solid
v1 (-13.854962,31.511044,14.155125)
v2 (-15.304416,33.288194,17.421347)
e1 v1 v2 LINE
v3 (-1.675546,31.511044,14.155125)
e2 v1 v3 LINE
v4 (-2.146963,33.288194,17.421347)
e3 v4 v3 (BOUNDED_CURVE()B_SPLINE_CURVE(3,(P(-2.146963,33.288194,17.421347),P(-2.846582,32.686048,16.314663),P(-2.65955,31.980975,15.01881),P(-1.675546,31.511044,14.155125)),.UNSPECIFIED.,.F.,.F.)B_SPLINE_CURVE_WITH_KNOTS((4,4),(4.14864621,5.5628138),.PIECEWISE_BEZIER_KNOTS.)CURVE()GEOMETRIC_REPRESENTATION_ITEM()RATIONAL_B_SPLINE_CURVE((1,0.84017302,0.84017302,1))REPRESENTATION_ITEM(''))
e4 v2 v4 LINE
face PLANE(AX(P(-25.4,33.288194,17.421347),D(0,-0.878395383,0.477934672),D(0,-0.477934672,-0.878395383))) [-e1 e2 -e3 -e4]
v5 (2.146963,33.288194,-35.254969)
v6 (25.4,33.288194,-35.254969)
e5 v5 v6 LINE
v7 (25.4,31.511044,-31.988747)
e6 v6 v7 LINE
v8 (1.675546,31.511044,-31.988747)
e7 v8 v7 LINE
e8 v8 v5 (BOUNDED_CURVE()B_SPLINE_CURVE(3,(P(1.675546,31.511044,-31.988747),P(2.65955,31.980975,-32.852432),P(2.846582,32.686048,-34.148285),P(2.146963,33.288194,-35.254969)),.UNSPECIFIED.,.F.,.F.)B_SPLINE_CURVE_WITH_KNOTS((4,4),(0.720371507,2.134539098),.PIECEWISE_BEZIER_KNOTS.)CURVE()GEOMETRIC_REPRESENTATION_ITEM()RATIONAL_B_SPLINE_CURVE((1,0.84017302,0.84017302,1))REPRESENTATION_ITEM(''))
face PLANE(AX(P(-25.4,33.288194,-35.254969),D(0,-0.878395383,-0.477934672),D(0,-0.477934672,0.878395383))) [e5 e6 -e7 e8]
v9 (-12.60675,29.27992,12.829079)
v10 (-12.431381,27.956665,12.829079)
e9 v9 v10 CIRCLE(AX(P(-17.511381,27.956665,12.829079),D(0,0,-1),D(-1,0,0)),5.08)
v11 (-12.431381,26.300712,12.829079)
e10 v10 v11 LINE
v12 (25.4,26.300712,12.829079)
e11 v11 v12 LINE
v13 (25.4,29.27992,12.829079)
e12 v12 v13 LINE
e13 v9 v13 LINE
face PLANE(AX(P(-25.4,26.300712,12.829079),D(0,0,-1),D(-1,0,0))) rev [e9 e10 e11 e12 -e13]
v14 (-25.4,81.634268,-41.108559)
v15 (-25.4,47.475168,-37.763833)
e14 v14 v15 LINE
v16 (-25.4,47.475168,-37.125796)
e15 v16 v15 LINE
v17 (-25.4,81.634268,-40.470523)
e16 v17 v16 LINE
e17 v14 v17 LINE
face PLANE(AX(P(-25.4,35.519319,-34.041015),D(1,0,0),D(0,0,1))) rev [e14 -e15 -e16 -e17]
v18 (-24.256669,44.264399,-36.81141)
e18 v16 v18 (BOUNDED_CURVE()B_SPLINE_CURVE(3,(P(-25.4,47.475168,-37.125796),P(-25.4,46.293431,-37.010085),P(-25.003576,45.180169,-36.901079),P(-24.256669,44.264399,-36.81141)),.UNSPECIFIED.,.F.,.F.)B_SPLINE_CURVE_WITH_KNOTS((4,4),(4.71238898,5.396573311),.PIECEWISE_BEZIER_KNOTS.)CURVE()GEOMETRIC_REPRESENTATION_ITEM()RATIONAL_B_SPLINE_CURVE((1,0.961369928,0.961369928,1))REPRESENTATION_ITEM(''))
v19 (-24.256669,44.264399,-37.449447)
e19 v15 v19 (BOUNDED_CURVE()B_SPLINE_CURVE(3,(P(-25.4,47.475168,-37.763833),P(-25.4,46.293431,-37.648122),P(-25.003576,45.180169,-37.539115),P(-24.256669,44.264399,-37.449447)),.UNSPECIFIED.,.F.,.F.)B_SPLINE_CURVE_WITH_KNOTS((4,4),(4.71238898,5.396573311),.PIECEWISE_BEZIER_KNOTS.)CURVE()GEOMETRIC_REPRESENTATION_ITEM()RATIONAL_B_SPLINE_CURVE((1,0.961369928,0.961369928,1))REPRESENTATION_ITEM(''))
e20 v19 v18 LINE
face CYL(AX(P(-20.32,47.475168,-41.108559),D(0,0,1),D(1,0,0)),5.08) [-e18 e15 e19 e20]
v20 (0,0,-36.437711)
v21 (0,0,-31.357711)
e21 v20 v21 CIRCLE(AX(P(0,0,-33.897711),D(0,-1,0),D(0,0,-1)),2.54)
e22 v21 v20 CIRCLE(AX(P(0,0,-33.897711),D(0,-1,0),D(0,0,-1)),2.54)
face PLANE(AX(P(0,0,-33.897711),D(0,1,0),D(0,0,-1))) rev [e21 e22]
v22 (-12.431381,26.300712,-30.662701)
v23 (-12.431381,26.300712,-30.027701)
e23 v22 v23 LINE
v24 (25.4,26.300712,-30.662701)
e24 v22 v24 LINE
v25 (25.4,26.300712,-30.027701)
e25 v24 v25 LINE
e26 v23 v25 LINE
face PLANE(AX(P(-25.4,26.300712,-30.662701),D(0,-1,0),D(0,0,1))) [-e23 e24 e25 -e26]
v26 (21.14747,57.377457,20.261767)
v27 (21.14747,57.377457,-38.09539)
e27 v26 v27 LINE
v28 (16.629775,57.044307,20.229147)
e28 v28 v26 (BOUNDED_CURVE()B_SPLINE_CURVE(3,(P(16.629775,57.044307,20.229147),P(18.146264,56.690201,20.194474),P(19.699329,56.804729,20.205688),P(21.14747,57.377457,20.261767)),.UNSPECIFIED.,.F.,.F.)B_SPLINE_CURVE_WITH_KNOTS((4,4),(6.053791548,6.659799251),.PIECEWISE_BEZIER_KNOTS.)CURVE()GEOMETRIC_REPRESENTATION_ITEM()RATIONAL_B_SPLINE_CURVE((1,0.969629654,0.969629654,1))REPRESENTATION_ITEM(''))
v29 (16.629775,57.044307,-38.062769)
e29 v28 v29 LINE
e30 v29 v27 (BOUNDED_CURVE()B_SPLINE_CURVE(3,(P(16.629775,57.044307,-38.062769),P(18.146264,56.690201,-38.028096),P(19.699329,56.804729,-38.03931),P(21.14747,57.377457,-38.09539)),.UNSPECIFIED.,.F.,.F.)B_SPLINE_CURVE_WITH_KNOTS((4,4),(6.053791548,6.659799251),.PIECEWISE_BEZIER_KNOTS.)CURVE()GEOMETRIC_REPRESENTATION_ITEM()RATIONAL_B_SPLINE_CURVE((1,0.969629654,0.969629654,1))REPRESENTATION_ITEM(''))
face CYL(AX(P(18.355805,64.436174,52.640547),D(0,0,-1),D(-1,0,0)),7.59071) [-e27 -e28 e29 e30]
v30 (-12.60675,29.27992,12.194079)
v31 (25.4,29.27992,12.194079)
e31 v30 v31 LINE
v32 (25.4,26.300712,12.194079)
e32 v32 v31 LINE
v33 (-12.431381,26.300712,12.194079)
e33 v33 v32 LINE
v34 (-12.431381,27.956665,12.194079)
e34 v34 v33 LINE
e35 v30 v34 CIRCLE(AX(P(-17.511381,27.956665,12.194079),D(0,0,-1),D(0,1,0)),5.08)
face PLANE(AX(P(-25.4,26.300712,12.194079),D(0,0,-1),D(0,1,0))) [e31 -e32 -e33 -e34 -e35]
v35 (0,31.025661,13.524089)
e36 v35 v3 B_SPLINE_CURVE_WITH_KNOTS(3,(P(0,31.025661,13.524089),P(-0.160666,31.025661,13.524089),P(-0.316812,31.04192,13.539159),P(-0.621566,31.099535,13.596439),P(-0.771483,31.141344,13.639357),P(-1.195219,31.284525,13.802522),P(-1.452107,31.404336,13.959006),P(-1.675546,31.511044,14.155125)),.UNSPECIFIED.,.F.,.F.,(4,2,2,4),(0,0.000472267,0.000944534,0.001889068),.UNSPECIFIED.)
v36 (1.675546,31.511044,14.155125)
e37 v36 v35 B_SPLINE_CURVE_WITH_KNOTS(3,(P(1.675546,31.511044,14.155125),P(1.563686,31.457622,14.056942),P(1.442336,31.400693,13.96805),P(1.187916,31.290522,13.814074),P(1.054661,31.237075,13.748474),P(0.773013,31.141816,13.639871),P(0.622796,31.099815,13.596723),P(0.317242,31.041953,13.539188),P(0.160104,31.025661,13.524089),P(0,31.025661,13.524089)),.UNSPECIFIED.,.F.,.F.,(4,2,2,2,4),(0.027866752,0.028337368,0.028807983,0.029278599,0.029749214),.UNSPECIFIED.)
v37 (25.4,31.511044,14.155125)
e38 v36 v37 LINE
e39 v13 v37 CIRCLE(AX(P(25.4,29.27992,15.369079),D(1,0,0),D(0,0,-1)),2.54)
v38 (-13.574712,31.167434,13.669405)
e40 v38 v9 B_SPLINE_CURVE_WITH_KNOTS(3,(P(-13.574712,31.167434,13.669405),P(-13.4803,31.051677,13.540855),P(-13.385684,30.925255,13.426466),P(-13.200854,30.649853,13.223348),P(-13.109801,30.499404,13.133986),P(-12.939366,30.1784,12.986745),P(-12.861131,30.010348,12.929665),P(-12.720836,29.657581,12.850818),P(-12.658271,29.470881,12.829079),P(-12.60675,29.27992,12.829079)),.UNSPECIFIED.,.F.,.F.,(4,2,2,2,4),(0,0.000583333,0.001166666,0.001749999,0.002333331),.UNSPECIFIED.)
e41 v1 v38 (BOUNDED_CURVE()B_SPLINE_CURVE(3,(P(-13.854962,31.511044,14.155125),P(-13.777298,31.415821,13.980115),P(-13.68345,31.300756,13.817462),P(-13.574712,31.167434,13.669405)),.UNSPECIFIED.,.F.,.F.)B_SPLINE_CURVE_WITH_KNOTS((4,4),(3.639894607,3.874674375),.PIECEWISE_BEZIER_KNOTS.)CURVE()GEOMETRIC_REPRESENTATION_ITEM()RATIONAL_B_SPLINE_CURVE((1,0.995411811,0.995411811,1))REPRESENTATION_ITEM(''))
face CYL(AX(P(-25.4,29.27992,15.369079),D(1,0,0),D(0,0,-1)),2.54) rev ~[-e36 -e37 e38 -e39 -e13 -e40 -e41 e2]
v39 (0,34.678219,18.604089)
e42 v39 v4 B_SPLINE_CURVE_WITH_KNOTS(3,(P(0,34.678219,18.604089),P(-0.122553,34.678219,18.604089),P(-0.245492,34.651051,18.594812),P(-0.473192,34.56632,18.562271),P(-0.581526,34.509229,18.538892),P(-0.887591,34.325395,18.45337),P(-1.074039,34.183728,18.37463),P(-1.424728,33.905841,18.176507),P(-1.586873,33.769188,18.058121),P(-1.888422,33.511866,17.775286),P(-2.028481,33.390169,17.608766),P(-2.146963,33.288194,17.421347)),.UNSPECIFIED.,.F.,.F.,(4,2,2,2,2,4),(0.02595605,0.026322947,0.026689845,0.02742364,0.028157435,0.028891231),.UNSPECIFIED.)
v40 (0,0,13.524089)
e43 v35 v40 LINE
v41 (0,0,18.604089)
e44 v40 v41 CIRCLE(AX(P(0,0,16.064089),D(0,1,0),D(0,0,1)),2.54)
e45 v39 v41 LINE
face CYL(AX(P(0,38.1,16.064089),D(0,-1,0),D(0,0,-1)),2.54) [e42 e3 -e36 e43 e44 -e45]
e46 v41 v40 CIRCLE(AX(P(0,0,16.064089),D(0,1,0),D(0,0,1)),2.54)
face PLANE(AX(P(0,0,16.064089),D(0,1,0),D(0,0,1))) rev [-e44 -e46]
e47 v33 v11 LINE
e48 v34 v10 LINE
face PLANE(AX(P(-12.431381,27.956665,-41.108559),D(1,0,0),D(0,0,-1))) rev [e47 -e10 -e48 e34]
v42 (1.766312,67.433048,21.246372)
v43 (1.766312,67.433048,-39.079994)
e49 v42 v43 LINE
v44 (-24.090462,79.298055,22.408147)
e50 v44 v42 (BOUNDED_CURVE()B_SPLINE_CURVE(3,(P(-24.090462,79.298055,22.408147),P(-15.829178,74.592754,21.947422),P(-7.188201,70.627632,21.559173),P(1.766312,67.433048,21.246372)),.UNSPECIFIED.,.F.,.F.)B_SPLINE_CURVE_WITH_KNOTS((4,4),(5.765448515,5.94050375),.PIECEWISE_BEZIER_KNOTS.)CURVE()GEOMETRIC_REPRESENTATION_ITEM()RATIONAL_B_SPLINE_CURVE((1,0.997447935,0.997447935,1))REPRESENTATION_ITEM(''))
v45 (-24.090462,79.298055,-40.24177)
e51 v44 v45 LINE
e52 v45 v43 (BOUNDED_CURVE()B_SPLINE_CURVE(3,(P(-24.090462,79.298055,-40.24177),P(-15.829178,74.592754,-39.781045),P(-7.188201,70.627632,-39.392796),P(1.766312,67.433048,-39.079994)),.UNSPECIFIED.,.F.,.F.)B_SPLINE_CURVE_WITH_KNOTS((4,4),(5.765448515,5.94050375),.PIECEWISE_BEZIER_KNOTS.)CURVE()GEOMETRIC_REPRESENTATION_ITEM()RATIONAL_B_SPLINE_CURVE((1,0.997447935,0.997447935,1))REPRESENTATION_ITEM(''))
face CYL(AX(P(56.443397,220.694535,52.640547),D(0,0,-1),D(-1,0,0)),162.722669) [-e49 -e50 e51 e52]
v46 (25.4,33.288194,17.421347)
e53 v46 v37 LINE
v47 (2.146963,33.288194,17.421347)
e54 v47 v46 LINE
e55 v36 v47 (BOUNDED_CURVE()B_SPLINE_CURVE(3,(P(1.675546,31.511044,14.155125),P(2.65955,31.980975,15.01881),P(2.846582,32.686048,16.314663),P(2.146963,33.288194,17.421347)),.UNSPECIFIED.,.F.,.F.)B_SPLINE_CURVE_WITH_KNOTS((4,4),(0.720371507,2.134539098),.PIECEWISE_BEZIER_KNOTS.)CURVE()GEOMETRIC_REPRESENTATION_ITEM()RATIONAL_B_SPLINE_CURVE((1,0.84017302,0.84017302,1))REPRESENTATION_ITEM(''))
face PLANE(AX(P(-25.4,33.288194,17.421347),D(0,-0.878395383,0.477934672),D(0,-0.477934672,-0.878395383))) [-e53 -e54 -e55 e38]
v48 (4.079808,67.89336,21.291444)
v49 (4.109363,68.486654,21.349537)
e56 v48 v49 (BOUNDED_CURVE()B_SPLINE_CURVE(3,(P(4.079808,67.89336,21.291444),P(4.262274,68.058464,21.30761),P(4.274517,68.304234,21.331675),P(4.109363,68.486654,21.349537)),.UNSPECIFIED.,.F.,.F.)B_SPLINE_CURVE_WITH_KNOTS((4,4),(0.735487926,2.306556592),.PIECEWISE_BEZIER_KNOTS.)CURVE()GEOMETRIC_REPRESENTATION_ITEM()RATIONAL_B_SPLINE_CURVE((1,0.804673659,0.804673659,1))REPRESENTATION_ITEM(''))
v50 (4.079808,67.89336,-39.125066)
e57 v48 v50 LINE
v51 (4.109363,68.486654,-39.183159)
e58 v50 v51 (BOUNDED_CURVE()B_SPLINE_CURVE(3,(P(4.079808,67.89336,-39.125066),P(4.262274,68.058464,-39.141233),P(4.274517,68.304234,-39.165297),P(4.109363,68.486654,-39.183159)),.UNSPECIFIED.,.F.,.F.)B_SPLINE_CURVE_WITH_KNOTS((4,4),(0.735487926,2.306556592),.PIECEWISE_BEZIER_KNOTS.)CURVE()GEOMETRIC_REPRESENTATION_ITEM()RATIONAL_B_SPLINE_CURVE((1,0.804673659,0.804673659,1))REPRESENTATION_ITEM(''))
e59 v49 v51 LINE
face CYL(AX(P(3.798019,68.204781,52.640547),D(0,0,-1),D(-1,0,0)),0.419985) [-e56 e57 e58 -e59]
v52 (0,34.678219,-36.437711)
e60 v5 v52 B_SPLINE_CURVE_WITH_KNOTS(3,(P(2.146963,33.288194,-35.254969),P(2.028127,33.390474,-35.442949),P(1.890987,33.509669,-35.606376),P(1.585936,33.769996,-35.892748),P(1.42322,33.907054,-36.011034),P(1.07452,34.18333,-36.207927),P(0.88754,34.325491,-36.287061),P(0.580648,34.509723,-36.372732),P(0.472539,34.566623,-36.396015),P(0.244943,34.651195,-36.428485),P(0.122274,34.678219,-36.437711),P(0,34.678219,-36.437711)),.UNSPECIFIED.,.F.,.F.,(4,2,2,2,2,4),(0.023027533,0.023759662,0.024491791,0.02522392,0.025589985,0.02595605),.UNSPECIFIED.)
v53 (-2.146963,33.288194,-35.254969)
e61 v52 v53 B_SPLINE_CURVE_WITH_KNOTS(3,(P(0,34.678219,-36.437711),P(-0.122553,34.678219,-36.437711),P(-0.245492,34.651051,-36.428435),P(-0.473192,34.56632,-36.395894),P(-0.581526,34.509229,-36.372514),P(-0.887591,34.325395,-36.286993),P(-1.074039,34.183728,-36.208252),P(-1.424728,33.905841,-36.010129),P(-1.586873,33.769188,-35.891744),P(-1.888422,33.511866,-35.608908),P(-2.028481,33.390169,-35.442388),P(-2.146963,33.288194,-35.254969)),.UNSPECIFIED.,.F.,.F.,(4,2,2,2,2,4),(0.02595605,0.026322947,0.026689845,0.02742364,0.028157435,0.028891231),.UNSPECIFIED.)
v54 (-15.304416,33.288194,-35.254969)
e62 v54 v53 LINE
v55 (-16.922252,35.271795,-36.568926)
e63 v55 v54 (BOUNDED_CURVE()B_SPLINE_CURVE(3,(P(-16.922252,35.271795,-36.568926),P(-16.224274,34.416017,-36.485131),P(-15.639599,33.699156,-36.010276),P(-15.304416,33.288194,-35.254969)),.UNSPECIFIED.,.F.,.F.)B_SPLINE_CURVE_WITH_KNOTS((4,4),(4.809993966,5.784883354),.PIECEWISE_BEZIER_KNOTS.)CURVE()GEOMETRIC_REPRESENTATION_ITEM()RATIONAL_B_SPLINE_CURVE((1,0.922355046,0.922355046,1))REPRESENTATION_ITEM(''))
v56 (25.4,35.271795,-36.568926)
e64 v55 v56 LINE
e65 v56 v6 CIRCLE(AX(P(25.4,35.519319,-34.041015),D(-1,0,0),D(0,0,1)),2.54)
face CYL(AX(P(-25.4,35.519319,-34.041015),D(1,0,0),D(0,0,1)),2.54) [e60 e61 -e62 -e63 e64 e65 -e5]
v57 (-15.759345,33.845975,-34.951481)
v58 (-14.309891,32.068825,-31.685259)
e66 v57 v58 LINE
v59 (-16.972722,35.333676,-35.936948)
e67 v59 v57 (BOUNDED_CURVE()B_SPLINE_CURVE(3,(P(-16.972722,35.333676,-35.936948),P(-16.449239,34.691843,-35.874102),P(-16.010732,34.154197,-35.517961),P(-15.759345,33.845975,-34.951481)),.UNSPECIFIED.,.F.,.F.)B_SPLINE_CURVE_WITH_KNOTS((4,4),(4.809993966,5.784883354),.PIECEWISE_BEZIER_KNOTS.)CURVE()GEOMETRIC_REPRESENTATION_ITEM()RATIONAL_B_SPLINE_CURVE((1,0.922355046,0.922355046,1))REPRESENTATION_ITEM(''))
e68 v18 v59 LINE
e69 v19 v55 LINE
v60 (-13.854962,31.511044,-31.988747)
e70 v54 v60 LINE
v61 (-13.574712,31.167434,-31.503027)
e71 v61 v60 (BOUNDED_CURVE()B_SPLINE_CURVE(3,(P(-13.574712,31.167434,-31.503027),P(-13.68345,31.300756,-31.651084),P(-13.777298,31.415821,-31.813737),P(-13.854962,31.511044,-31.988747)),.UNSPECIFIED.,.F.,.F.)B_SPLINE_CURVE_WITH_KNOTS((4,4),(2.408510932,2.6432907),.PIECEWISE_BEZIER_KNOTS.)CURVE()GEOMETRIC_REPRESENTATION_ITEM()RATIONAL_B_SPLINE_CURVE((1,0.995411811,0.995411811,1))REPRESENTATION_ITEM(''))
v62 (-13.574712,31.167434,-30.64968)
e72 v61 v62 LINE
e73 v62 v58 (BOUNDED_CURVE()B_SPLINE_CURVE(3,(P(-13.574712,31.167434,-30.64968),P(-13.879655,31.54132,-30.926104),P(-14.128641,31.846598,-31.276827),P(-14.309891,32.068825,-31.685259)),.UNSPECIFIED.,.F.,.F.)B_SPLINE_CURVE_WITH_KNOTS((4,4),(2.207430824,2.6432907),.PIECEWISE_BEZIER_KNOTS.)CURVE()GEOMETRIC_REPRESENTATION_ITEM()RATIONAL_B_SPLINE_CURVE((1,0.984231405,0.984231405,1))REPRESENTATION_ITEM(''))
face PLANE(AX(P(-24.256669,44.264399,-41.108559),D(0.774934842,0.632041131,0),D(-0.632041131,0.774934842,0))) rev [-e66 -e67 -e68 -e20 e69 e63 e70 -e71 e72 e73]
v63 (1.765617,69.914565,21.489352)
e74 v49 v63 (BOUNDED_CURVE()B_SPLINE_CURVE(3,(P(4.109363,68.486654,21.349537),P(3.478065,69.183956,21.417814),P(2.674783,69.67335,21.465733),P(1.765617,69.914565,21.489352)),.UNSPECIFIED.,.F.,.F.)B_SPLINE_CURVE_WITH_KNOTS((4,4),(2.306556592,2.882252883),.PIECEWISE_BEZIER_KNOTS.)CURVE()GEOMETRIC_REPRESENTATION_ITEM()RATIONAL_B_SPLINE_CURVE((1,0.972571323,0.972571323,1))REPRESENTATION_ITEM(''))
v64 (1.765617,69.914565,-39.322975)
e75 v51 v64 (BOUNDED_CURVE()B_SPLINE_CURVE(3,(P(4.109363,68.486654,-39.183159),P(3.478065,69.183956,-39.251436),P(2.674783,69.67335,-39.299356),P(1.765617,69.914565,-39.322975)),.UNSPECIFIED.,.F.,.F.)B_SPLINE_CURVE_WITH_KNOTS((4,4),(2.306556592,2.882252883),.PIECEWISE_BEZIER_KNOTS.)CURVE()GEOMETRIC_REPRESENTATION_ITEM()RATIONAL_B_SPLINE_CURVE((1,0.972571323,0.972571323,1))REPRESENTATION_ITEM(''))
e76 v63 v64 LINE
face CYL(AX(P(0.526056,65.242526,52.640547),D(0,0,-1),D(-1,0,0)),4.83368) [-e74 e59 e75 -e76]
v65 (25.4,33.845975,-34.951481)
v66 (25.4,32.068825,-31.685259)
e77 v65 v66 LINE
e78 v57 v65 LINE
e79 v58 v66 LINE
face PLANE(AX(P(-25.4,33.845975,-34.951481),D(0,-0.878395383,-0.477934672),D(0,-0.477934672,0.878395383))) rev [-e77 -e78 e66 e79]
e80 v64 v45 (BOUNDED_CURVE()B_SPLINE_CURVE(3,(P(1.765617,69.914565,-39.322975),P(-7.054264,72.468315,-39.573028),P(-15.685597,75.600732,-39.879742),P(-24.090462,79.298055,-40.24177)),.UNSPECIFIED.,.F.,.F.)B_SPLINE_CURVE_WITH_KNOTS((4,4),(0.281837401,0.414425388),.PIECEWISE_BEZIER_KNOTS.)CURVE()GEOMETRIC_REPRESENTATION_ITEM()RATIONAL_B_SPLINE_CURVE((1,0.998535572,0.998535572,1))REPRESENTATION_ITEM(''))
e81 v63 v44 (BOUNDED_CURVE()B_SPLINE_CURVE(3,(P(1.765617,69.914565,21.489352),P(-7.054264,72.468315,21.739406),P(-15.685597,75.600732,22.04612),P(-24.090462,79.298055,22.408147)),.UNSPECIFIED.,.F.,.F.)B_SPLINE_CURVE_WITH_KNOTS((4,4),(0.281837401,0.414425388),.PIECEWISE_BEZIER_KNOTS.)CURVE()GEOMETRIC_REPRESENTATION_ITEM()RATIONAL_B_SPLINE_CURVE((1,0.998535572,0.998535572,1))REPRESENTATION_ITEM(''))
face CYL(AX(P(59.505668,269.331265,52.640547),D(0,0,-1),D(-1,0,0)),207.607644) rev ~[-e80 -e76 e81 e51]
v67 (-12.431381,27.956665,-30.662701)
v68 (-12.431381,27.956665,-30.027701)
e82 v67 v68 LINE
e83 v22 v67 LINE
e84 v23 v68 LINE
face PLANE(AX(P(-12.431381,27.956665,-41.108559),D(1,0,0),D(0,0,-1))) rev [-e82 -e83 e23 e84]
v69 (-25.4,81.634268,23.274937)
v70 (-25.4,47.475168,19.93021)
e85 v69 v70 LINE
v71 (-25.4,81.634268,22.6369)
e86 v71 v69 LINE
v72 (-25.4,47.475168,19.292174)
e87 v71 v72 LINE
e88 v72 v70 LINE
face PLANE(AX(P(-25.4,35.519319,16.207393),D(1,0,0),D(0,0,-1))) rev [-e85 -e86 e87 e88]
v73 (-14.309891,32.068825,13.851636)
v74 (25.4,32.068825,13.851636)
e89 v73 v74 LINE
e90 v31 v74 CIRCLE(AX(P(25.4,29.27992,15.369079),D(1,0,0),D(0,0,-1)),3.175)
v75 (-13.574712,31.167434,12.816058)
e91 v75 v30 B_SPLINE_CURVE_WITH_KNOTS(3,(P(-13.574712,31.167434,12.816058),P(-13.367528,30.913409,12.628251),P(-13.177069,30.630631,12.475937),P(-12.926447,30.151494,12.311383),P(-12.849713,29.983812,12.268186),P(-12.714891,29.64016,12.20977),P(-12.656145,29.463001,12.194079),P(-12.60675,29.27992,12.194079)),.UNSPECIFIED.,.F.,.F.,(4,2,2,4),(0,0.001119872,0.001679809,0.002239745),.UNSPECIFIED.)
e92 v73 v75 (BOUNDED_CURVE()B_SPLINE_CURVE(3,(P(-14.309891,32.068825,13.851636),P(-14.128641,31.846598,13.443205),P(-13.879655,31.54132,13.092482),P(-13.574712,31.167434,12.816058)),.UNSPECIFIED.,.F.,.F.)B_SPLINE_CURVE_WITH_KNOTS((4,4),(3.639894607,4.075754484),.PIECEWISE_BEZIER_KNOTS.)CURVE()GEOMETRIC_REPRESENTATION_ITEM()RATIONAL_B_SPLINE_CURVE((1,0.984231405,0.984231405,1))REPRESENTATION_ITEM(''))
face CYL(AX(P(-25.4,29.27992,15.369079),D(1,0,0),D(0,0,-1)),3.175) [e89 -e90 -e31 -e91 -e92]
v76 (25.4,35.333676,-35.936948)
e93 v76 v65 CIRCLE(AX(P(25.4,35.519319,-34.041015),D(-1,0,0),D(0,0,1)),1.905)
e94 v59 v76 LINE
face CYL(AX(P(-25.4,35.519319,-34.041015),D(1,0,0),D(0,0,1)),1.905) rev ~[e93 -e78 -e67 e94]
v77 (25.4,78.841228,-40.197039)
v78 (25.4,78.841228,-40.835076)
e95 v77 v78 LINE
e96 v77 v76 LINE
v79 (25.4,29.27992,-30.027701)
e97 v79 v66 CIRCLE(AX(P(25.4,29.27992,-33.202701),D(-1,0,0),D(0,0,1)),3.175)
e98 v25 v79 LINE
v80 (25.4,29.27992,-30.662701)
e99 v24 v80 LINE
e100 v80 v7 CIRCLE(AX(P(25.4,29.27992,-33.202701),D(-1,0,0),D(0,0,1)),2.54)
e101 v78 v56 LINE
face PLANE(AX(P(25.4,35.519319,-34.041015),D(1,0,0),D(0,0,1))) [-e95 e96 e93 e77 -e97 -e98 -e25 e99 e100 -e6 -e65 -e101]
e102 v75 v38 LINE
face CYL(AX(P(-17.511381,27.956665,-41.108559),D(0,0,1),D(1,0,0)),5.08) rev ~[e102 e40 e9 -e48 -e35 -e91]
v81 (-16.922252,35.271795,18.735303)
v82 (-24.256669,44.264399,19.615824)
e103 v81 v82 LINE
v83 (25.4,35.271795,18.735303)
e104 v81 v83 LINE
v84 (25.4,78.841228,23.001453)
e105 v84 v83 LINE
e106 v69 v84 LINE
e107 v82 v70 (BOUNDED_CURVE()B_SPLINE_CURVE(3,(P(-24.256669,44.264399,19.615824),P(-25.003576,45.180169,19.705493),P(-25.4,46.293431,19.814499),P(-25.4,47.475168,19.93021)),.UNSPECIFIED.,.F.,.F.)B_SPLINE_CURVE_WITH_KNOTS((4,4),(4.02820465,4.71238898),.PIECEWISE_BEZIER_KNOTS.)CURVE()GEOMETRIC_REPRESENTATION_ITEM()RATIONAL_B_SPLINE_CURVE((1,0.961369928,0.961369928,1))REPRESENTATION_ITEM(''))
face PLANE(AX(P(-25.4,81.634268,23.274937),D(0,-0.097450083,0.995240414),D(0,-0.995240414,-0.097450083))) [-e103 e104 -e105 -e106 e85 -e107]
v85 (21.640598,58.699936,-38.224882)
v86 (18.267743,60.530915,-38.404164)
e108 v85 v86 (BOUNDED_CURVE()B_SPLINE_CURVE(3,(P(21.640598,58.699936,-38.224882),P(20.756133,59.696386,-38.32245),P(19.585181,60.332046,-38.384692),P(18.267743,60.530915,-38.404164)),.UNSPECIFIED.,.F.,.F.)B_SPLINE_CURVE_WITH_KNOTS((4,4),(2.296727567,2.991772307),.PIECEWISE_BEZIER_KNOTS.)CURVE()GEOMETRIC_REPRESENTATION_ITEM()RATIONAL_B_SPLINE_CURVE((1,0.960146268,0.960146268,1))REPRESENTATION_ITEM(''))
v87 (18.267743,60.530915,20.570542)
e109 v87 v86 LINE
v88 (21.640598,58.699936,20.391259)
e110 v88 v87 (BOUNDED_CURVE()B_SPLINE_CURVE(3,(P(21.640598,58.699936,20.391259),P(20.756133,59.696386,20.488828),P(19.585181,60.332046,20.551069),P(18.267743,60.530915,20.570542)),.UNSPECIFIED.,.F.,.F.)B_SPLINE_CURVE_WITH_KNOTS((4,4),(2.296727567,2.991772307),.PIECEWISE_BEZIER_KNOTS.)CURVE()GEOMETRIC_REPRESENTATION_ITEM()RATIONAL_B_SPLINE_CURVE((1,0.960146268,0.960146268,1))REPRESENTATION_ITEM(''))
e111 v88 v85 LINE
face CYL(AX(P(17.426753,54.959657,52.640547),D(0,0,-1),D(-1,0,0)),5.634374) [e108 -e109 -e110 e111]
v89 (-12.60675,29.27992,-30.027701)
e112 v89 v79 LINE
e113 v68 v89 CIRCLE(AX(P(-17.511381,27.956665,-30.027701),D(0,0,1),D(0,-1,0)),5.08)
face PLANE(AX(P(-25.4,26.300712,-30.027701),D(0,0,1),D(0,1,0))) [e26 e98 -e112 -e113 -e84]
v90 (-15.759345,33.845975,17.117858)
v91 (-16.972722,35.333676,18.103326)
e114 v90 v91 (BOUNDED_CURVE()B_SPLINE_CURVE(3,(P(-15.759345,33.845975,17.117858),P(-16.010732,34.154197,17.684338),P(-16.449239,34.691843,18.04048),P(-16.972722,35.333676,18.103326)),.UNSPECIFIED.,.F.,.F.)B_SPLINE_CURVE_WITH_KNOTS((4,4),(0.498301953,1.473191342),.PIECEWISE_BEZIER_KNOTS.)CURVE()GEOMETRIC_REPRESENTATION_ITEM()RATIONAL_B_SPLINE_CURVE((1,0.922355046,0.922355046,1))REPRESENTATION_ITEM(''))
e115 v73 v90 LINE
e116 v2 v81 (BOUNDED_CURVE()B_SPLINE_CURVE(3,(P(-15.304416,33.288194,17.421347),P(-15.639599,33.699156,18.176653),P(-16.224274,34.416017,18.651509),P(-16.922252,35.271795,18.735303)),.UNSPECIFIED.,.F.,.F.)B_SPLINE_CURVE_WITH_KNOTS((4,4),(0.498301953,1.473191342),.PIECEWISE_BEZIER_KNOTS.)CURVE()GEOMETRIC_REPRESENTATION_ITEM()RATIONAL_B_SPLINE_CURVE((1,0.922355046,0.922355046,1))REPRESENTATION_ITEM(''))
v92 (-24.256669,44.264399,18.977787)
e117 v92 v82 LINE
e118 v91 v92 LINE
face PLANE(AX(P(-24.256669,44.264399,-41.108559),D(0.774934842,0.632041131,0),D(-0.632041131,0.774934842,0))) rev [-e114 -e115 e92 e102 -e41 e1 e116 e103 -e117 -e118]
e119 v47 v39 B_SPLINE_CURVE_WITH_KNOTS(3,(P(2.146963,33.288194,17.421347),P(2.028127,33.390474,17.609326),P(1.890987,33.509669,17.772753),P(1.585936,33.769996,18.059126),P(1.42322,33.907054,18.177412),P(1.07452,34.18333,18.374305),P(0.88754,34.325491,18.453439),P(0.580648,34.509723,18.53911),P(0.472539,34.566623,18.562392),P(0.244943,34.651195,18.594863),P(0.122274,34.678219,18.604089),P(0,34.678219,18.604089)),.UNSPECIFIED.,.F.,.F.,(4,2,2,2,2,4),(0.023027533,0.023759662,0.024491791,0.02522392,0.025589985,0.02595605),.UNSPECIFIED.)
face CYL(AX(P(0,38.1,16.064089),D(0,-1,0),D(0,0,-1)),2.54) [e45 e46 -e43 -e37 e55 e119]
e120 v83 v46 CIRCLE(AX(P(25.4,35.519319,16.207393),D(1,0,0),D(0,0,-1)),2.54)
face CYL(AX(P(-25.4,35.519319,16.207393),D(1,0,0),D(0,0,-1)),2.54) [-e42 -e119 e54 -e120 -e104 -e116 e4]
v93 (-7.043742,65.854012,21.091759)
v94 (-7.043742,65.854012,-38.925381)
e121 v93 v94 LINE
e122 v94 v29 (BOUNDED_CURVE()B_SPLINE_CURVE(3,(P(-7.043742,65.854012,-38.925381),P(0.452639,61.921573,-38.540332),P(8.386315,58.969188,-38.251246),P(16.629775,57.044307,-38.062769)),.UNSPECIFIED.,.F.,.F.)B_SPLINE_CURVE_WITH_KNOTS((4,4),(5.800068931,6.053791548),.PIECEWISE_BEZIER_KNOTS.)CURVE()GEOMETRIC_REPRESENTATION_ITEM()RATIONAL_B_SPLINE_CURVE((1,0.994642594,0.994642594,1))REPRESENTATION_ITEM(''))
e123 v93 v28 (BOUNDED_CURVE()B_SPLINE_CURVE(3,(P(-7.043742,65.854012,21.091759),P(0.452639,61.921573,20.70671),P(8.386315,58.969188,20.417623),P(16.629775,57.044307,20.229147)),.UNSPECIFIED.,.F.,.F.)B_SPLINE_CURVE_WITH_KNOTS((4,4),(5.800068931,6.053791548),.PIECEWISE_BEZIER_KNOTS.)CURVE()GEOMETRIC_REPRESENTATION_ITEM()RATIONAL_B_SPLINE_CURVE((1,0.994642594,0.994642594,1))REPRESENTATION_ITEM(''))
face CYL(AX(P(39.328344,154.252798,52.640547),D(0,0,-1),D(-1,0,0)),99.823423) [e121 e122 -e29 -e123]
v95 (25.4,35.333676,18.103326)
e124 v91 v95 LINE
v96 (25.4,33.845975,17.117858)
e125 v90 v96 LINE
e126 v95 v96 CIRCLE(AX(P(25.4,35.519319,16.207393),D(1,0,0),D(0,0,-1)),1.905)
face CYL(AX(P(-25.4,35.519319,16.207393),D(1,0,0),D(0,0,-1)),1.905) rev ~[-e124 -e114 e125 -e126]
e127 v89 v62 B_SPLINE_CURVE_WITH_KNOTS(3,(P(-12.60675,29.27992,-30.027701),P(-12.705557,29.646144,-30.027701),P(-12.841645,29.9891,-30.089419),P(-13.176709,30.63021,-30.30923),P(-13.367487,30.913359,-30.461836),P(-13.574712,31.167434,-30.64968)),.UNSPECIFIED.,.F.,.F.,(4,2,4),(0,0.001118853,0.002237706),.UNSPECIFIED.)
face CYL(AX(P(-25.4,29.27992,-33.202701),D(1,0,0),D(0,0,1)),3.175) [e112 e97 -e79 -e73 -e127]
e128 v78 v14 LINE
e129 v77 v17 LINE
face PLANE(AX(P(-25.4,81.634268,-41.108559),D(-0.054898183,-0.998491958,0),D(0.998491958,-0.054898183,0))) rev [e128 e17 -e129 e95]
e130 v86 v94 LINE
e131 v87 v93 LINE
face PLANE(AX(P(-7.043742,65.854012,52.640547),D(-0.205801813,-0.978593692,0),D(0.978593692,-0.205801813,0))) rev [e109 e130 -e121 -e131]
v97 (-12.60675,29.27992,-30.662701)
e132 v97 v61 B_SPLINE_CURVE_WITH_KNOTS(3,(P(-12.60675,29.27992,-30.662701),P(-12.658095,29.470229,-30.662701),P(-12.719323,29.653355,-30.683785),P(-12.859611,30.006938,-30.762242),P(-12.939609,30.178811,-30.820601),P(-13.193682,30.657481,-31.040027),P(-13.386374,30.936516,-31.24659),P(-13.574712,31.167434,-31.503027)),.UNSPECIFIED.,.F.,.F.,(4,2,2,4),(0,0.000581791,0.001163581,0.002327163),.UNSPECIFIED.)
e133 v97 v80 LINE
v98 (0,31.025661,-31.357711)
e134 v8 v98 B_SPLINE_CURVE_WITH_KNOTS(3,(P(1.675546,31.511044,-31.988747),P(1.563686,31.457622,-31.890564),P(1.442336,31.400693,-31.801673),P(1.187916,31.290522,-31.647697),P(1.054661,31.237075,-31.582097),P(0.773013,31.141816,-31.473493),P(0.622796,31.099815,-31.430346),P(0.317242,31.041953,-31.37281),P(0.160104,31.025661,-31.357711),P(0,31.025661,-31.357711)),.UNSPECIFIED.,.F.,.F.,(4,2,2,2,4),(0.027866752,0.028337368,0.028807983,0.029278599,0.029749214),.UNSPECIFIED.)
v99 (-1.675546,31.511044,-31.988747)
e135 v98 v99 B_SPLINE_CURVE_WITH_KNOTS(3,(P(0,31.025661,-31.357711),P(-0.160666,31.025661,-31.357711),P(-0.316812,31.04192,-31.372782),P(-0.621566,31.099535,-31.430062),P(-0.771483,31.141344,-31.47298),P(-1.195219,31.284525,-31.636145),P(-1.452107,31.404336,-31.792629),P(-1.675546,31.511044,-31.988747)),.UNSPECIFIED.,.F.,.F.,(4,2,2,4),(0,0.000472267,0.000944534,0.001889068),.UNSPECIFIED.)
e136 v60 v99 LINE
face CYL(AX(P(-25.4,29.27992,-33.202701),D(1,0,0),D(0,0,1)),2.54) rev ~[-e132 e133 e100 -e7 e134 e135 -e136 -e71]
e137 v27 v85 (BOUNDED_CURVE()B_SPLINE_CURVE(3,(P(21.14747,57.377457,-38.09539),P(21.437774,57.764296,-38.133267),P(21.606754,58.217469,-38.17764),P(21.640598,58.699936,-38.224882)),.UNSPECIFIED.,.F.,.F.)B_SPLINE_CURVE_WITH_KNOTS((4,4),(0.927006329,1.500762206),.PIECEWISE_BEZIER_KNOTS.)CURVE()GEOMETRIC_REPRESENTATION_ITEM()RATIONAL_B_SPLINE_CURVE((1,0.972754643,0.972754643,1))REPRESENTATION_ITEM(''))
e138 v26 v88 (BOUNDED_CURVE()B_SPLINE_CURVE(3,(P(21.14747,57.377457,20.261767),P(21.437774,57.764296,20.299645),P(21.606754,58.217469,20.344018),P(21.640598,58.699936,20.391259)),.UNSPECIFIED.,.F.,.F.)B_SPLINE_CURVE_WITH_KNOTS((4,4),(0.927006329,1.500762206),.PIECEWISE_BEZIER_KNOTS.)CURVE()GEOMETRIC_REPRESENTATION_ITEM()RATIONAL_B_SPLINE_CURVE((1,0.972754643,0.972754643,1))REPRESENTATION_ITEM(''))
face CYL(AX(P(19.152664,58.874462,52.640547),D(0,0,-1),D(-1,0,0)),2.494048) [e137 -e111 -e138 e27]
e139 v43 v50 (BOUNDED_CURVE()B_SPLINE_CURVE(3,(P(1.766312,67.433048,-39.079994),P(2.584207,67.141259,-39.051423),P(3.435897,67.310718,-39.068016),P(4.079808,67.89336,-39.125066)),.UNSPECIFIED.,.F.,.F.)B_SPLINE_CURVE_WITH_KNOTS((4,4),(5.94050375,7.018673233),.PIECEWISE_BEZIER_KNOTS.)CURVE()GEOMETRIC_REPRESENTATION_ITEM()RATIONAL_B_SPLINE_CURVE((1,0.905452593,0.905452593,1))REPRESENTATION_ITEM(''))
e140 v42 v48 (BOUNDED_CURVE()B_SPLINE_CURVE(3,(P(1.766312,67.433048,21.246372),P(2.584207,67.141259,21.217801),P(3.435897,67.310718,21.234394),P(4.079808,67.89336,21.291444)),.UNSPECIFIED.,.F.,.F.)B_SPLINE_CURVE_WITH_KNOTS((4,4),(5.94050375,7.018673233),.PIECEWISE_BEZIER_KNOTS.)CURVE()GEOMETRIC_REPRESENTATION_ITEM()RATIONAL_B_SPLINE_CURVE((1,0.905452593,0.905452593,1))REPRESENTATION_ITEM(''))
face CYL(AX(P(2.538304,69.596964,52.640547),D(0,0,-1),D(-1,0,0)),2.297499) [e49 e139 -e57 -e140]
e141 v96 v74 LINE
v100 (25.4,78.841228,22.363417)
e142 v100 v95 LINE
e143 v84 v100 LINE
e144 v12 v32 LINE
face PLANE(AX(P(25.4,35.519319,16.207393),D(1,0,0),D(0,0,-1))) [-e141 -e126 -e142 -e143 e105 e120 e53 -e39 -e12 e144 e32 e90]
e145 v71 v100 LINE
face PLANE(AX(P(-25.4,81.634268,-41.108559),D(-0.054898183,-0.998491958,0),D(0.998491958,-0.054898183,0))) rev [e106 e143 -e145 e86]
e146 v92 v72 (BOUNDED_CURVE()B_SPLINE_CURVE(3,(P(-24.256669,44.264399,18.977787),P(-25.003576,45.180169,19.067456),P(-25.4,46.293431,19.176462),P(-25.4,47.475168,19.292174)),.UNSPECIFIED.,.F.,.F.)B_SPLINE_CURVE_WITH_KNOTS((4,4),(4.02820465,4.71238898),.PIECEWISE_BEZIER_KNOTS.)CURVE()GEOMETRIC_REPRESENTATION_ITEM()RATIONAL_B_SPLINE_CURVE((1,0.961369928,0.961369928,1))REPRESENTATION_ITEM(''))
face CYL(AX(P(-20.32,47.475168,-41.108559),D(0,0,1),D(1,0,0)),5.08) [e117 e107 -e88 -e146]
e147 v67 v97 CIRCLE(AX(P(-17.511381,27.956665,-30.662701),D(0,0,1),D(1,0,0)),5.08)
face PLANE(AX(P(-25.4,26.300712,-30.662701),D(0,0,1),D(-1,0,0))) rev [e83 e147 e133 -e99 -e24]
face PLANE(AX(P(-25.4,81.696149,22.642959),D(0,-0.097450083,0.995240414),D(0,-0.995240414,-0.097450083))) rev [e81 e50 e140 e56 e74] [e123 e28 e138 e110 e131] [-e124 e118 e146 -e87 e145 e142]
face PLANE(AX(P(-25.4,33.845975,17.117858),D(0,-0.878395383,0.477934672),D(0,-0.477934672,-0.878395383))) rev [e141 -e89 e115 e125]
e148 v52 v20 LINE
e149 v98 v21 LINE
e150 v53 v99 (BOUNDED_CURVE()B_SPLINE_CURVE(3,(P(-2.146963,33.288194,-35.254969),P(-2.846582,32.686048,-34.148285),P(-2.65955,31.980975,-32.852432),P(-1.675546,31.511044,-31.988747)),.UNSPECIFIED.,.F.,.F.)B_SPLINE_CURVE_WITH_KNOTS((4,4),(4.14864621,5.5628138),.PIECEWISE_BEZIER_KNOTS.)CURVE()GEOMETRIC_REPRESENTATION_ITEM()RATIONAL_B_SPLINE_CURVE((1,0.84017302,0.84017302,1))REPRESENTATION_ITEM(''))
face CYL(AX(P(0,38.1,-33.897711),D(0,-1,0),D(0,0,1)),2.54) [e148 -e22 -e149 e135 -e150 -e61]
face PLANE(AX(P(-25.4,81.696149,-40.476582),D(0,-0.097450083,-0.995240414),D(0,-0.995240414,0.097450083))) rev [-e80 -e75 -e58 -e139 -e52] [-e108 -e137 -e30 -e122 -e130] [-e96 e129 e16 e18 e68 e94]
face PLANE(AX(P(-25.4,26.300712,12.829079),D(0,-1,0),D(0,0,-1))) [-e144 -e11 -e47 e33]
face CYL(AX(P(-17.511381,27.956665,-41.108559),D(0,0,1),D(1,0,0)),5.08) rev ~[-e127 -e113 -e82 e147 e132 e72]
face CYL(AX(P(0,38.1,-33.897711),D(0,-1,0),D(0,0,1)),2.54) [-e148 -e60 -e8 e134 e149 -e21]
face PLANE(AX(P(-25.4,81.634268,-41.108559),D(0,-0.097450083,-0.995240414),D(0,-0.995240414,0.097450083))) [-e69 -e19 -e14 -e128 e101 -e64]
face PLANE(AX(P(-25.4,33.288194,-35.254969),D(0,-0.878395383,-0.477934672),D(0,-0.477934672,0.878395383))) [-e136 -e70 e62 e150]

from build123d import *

# Parameters (mm, degrees)
SKETCH2_R                       = 2.54
BOSS_EXTRUDE1_DEPTH             = 38.1
BOSS_EXTRUDE2_DEPTH             = 25.4
BOSS_EXTRUDE2_DEPTH_BACK        = 25.4
CUT_EXTRUDE1_DEPTH              = 69.088
BOSS_EXTRUDE3_REACH             = 96.918
BOSS_EXTRUDE3_DIRECTION_2_REACH = 96.918
CUT_EXTRUDE2_DEPTH              = 95.917513418
CUT_EXTRUDE2_DEPTH_BACK         = 95.917513418


with BuildPart() as part:
    # Sketch2 → Boss-Extrude1 (new body)
    with BuildSketch(Plane(origin=(0, 0, 0), x_dir=(1, 0, 0), z_dir=(0, 1, 0))):
        with Locations(Location((0, -16.064088759, 0), (0, 0, 90))):
            Circle(SKETCH2_R)
    extrude(amount=BOSS_EXTRUDE1_DEPTH)

    # Sketch3 → Boss-Extrude2 (add, two sides: drawn at the far end of the back side and taken through both)
    with BuildSketch(Plane(origin=(0, 0, 0), x_dir=(0, 0, -1), z_dir=(1, 0, 0)).offset(-BOSS_EXTRUDE2_DEPTH_BACK)):
        with BuildLine():
            Line((-12.829078619, 26.300712117), (-12.829078619, 29.279919525))
            ThreePointArc((-12.829078619, 29.279919525), (-13.185613102, 30.577639963), (-14.155124552, 31.511043798))
            Line((-14.155124552, 31.511043798), (-17.42134678, 33.28819436))
            ThreePointArc((-17.42134678, 33.28819436), (-18.324951729, 34.116627002), (-18.735303364, 35.271795423))
            Line((-18.735303364, 35.271795423), (-23.274936915, 81.634267777))
            Line((-23.274936915, 81.634267777), (-22.642959252, 81.696148579))
            Line((-22.642959252, 81.696148579), (-18.103325701, 35.333676225))
            ThreePointArc((-18.103325701, 35.333676225), (-17.795561975, 34.467299909), (-17.117858263, 33.845975428))
            Line((-17.117858263, 33.845975428), (-13.851636036, 32.068824867))
            ThreePointArc((-13.851636036, 32.068824867), (-12.639746723, 30.902070072), (-12.194078619, 29.279919525))
            Line((-12.194078619, 29.279919525), (-12.194078619, 26.300712117))
            Line((-12.194078619, 26.300712117), (-12.829078619, 26.300712117))
        make_face()
    extrude(amount=BOSS_EXTRUDE2_DEPTH + BOSS_EXTRUDE2_DEPTH_BACK)

    # Sketch4 → Cut-Extrude1 (cut)
    with BuildSketch(Plane.ZY.offset(25.4)):
        with BuildLine():
            Line((18.518981342, 39.578693563), (18.103325701, 35.333676225))
            ThreePointArc((18.103325701, 35.333676225), (17.795561975, 34.467299909), (17.117858263, 33.845975428))
            Line((17.117858263, 33.845975428), (13.851636036, 32.068824867))
            ThreePointArc((13.851636036, 32.068824867), (12.639746723, 30.902070072), (12.194078619, 29.279919525))
            Line((12.194078619, 29.279919525), (9.661418427, 39.233443058))
            Line((9.661418427, 39.233443058), (18.518981342, 39.578693563))
        make_face()
    extrude(amount=-CUT_EXTRUDE1_DEPTH, mode=Mode.SUBTRACT)


with BuildPart() as body_2:
    # Mirror3: mirrored copy
    add(part.part.mirror(Plane.XY.offset(-8.916811241)))


with BuildPart() as part_1:
    add(part.part)

    add(body_2.part)  # Boss-Extrude3 merges body 2
    # Boss-Extrude3: up to this plane
    boss_extrude3_end = Plane(origin=(-25.4, 81.696148579, 22.642959252), z_dir=(0, -0.09745008287838285, 0.9952404138433066))
    # Sketch7 → Boss-Extrude3 (add, up to the surface)
    with BuildSketch(Plane.XY, mode=Mode.PRIVATE) as boss_extrude3_sk1:
        with BuildLine():
            Line((-7.043742341, 65.854012335), (18.267742921, 60.530914923))
            ThreePointArc((18.267742921, 60.530914923), (20.11486758, 59.911446579), (21.640598099, 58.699936398))
            ThreePointArc((21.640598099, 58.699936398), (21.489537489, 58.003085292), (21.14747004, 57.377457102))
            ThreePointArc((21.14747004, 57.377457102), (18.914053882, 56.866019856), (16.629775134, 57.044307226))
            ThreePointArc((16.629775134, 57.044307226), (4.513238392, 60.697337852), (-7.043742341, 65.854012335))
        make_face()
    boss_extrude3_tool1 = split(extrude(boss_extrude3_sk1.sketch, amount=BOSS_EXTRUDE3_REACH, mode=Mode.PRIVATE), bisect_by=boss_extrude3_end, keep=Keep.BOTH, mode=Mode.PRIVATE)
    add(boss_extrude3_tool1.solids().sort_by_distance((10.084711, 60.694895, 0))[0])
    # Sketch7 → Boss-Extrude3 (add, up to the surface)
    with BuildSketch(Plane.XY, mode=Mode.PRIVATE) as boss_extrude3_sk2:
        with BuildLine():
            ThreePointArc((-24.090462047, 79.298055074), (-11.317996693, 74.177627192), (1.76561715, 69.914564711))
            ThreePointArc((1.76561715, 69.914564711), (3.040960958, 69.370444609), (4.109363257, 68.486654453))
            ThreePointArc((4.109363257, 68.486654453), (4.217484646, 68.183885083), (4.079808176, 67.893360185))
            ThreePointArc((4.079808176, 67.893360185), (2.986644186, 67.343634533), (1.766311851, 67.433048138))
            ThreePointArc((1.766311851, 67.433048138), (-11.421869926, 72.799394657), (-24.090462047, 79.298055074))
        make_face()
    boss_extrude3_tool2 = split(extrude(boss_extrude3_sk2.sketch, amount=BOSS_EXTRUDE3_REACH, mode=Mode.PRIVATE), bisect_by=boss_extrude3_end, keep=Keep.BOTH, mode=Mode.PRIVATE)
    add(boss_extrude3_tool2.solids().sort_by_distance((-6.156417, 71.59743, 0))[0])

    # Boss-Extrude3 direction 2: up to this plane
    boss_extrude3_direction_2_end = Plane(origin=(-25.4, 81.696148579, -40.476581735), z_dir=(0, -0.09745008287838285, -0.9952404138433066))
    # Sketch7 → Boss-Extrude3 direction 2 (add, up to the surface)
    with BuildSketch(Plane.XY, mode=Mode.PRIVATE) as boss_extrude3_direction_2_sk1:
        with BuildLine():
            Line((-7.043742341, 65.854012335), (18.267742921, 60.530914923))
            ThreePointArc((18.267742921, 60.530914923), (20.11486758, 59.911446579), (21.640598099, 58.699936398))
            ThreePointArc((21.640598099, 58.699936398), (21.489537489, 58.003085292), (21.14747004, 57.377457102))
            ThreePointArc((21.14747004, 57.377457102), (18.914053882, 56.866019856), (16.629775134, 57.044307226))
            ThreePointArc((16.629775134, 57.044307226), (4.513238392, 60.697337852), (-7.043742341, 65.854012335))
        make_face()
    boss_extrude3_direction_2_tool1 = split(extrude(boss_extrude3_direction_2_sk1.sketch, amount=-BOSS_EXTRUDE3_DIRECTION_2_REACH, mode=Mode.PRIVATE), bisect_by=boss_extrude3_direction_2_end, keep=Keep.BOTH, mode=Mode.PRIVATE)
    add(boss_extrude3_direction_2_tool1.solids().sort_by_distance((10.084711, 60.694895, 0))[0])
    # Sketch7 → Boss-Extrude3 direction 2 (add, up to the surface)
    with BuildSketch(Plane.XY, mode=Mode.PRIVATE) as boss_extrude3_direction_2_sk2:
        with BuildLine():
            ThreePointArc((-24.090462047, 79.298055074), (-11.317996693, 74.177627192), (1.76561715, 69.914564711))
            ThreePointArc((1.76561715, 69.914564711), (3.040960958, 69.370444609), (4.109363257, 68.486654453))
            ThreePointArc((4.109363257, 68.486654453), (4.217484646, 68.183885083), (4.079808176, 67.893360185))
            ThreePointArc((4.079808176, 67.893360185), (2.986644186, 67.343634533), (1.766311851, 67.433048138))
            ThreePointArc((1.766311851, 67.433048138), (-11.421869926, 72.799394657), (-24.090462047, 79.298055074))
        make_face()
    boss_extrude3_direction_2_tool2 = split(extrude(boss_extrude3_direction_2_sk2.sketch, amount=-BOSS_EXTRUDE3_DIRECTION_2_REACH, mode=Mode.PRIVATE), bisect_by=boss_extrude3_direction_2_end, keep=Keep.BOTH, mode=Mode.PRIVATE)
    add(boss_extrude3_direction_2_tool2.solids().sort_by_distance((-6.156417, 71.59743, 0))[0])

    # Sketch8 → Cut-Extrude2 (cut, two sides: drawn at the far end of the back side and taken through both)
    with BuildSketch(Plane.XY.offset(-CUT_EXTRUDE2_DEPTH_BACK)):
        with BuildLine():
            Line((-24.256668996, 44.264399282), (-13.574711516, 31.167433557))
            ThreePointArc((-13.574711516, 31.167433557), (-12.725741657, 29.660795109), (-12.431380512, 27.956664612))
            Line((-12.431380512, 27.956664612), (-12.431380512, 22.730802701))
            Line((-12.431380512, 22.730802701), (-29.072503536, 23.334912896))
            Line((-29.072503536, 23.334912896), (-36.847334231, 46.202061997))
            Line((-36.847334231, 46.202061997), (-43.885114332, 82.767624865))
            Line((-43.885114332, 82.767624865), (28.390353763, 84.309501518))
            Line((28.390353763, 84.309501518), (29.354026671, 78.623831361))
            Line((29.354026671, 78.623831361), (-25.4, 81.634267777))
            Line((-25.4, 81.634267777), (-25.4, 51.141366203))
            Line((-25.4, 51.141366203), (-25.4, 47.475168227))
            ThreePointArc((-25.4, 47.475168227), (-25.105638855, 45.77103773), (-24.256668996, 44.264399282))
        make_face()
    extrude(amount=CUT_EXTRUDE2_DEPTH + CUT_EXTRUDE2_DEPTH_BACK, mode=Mode.SUBTRACT)


solid = part_1.part
